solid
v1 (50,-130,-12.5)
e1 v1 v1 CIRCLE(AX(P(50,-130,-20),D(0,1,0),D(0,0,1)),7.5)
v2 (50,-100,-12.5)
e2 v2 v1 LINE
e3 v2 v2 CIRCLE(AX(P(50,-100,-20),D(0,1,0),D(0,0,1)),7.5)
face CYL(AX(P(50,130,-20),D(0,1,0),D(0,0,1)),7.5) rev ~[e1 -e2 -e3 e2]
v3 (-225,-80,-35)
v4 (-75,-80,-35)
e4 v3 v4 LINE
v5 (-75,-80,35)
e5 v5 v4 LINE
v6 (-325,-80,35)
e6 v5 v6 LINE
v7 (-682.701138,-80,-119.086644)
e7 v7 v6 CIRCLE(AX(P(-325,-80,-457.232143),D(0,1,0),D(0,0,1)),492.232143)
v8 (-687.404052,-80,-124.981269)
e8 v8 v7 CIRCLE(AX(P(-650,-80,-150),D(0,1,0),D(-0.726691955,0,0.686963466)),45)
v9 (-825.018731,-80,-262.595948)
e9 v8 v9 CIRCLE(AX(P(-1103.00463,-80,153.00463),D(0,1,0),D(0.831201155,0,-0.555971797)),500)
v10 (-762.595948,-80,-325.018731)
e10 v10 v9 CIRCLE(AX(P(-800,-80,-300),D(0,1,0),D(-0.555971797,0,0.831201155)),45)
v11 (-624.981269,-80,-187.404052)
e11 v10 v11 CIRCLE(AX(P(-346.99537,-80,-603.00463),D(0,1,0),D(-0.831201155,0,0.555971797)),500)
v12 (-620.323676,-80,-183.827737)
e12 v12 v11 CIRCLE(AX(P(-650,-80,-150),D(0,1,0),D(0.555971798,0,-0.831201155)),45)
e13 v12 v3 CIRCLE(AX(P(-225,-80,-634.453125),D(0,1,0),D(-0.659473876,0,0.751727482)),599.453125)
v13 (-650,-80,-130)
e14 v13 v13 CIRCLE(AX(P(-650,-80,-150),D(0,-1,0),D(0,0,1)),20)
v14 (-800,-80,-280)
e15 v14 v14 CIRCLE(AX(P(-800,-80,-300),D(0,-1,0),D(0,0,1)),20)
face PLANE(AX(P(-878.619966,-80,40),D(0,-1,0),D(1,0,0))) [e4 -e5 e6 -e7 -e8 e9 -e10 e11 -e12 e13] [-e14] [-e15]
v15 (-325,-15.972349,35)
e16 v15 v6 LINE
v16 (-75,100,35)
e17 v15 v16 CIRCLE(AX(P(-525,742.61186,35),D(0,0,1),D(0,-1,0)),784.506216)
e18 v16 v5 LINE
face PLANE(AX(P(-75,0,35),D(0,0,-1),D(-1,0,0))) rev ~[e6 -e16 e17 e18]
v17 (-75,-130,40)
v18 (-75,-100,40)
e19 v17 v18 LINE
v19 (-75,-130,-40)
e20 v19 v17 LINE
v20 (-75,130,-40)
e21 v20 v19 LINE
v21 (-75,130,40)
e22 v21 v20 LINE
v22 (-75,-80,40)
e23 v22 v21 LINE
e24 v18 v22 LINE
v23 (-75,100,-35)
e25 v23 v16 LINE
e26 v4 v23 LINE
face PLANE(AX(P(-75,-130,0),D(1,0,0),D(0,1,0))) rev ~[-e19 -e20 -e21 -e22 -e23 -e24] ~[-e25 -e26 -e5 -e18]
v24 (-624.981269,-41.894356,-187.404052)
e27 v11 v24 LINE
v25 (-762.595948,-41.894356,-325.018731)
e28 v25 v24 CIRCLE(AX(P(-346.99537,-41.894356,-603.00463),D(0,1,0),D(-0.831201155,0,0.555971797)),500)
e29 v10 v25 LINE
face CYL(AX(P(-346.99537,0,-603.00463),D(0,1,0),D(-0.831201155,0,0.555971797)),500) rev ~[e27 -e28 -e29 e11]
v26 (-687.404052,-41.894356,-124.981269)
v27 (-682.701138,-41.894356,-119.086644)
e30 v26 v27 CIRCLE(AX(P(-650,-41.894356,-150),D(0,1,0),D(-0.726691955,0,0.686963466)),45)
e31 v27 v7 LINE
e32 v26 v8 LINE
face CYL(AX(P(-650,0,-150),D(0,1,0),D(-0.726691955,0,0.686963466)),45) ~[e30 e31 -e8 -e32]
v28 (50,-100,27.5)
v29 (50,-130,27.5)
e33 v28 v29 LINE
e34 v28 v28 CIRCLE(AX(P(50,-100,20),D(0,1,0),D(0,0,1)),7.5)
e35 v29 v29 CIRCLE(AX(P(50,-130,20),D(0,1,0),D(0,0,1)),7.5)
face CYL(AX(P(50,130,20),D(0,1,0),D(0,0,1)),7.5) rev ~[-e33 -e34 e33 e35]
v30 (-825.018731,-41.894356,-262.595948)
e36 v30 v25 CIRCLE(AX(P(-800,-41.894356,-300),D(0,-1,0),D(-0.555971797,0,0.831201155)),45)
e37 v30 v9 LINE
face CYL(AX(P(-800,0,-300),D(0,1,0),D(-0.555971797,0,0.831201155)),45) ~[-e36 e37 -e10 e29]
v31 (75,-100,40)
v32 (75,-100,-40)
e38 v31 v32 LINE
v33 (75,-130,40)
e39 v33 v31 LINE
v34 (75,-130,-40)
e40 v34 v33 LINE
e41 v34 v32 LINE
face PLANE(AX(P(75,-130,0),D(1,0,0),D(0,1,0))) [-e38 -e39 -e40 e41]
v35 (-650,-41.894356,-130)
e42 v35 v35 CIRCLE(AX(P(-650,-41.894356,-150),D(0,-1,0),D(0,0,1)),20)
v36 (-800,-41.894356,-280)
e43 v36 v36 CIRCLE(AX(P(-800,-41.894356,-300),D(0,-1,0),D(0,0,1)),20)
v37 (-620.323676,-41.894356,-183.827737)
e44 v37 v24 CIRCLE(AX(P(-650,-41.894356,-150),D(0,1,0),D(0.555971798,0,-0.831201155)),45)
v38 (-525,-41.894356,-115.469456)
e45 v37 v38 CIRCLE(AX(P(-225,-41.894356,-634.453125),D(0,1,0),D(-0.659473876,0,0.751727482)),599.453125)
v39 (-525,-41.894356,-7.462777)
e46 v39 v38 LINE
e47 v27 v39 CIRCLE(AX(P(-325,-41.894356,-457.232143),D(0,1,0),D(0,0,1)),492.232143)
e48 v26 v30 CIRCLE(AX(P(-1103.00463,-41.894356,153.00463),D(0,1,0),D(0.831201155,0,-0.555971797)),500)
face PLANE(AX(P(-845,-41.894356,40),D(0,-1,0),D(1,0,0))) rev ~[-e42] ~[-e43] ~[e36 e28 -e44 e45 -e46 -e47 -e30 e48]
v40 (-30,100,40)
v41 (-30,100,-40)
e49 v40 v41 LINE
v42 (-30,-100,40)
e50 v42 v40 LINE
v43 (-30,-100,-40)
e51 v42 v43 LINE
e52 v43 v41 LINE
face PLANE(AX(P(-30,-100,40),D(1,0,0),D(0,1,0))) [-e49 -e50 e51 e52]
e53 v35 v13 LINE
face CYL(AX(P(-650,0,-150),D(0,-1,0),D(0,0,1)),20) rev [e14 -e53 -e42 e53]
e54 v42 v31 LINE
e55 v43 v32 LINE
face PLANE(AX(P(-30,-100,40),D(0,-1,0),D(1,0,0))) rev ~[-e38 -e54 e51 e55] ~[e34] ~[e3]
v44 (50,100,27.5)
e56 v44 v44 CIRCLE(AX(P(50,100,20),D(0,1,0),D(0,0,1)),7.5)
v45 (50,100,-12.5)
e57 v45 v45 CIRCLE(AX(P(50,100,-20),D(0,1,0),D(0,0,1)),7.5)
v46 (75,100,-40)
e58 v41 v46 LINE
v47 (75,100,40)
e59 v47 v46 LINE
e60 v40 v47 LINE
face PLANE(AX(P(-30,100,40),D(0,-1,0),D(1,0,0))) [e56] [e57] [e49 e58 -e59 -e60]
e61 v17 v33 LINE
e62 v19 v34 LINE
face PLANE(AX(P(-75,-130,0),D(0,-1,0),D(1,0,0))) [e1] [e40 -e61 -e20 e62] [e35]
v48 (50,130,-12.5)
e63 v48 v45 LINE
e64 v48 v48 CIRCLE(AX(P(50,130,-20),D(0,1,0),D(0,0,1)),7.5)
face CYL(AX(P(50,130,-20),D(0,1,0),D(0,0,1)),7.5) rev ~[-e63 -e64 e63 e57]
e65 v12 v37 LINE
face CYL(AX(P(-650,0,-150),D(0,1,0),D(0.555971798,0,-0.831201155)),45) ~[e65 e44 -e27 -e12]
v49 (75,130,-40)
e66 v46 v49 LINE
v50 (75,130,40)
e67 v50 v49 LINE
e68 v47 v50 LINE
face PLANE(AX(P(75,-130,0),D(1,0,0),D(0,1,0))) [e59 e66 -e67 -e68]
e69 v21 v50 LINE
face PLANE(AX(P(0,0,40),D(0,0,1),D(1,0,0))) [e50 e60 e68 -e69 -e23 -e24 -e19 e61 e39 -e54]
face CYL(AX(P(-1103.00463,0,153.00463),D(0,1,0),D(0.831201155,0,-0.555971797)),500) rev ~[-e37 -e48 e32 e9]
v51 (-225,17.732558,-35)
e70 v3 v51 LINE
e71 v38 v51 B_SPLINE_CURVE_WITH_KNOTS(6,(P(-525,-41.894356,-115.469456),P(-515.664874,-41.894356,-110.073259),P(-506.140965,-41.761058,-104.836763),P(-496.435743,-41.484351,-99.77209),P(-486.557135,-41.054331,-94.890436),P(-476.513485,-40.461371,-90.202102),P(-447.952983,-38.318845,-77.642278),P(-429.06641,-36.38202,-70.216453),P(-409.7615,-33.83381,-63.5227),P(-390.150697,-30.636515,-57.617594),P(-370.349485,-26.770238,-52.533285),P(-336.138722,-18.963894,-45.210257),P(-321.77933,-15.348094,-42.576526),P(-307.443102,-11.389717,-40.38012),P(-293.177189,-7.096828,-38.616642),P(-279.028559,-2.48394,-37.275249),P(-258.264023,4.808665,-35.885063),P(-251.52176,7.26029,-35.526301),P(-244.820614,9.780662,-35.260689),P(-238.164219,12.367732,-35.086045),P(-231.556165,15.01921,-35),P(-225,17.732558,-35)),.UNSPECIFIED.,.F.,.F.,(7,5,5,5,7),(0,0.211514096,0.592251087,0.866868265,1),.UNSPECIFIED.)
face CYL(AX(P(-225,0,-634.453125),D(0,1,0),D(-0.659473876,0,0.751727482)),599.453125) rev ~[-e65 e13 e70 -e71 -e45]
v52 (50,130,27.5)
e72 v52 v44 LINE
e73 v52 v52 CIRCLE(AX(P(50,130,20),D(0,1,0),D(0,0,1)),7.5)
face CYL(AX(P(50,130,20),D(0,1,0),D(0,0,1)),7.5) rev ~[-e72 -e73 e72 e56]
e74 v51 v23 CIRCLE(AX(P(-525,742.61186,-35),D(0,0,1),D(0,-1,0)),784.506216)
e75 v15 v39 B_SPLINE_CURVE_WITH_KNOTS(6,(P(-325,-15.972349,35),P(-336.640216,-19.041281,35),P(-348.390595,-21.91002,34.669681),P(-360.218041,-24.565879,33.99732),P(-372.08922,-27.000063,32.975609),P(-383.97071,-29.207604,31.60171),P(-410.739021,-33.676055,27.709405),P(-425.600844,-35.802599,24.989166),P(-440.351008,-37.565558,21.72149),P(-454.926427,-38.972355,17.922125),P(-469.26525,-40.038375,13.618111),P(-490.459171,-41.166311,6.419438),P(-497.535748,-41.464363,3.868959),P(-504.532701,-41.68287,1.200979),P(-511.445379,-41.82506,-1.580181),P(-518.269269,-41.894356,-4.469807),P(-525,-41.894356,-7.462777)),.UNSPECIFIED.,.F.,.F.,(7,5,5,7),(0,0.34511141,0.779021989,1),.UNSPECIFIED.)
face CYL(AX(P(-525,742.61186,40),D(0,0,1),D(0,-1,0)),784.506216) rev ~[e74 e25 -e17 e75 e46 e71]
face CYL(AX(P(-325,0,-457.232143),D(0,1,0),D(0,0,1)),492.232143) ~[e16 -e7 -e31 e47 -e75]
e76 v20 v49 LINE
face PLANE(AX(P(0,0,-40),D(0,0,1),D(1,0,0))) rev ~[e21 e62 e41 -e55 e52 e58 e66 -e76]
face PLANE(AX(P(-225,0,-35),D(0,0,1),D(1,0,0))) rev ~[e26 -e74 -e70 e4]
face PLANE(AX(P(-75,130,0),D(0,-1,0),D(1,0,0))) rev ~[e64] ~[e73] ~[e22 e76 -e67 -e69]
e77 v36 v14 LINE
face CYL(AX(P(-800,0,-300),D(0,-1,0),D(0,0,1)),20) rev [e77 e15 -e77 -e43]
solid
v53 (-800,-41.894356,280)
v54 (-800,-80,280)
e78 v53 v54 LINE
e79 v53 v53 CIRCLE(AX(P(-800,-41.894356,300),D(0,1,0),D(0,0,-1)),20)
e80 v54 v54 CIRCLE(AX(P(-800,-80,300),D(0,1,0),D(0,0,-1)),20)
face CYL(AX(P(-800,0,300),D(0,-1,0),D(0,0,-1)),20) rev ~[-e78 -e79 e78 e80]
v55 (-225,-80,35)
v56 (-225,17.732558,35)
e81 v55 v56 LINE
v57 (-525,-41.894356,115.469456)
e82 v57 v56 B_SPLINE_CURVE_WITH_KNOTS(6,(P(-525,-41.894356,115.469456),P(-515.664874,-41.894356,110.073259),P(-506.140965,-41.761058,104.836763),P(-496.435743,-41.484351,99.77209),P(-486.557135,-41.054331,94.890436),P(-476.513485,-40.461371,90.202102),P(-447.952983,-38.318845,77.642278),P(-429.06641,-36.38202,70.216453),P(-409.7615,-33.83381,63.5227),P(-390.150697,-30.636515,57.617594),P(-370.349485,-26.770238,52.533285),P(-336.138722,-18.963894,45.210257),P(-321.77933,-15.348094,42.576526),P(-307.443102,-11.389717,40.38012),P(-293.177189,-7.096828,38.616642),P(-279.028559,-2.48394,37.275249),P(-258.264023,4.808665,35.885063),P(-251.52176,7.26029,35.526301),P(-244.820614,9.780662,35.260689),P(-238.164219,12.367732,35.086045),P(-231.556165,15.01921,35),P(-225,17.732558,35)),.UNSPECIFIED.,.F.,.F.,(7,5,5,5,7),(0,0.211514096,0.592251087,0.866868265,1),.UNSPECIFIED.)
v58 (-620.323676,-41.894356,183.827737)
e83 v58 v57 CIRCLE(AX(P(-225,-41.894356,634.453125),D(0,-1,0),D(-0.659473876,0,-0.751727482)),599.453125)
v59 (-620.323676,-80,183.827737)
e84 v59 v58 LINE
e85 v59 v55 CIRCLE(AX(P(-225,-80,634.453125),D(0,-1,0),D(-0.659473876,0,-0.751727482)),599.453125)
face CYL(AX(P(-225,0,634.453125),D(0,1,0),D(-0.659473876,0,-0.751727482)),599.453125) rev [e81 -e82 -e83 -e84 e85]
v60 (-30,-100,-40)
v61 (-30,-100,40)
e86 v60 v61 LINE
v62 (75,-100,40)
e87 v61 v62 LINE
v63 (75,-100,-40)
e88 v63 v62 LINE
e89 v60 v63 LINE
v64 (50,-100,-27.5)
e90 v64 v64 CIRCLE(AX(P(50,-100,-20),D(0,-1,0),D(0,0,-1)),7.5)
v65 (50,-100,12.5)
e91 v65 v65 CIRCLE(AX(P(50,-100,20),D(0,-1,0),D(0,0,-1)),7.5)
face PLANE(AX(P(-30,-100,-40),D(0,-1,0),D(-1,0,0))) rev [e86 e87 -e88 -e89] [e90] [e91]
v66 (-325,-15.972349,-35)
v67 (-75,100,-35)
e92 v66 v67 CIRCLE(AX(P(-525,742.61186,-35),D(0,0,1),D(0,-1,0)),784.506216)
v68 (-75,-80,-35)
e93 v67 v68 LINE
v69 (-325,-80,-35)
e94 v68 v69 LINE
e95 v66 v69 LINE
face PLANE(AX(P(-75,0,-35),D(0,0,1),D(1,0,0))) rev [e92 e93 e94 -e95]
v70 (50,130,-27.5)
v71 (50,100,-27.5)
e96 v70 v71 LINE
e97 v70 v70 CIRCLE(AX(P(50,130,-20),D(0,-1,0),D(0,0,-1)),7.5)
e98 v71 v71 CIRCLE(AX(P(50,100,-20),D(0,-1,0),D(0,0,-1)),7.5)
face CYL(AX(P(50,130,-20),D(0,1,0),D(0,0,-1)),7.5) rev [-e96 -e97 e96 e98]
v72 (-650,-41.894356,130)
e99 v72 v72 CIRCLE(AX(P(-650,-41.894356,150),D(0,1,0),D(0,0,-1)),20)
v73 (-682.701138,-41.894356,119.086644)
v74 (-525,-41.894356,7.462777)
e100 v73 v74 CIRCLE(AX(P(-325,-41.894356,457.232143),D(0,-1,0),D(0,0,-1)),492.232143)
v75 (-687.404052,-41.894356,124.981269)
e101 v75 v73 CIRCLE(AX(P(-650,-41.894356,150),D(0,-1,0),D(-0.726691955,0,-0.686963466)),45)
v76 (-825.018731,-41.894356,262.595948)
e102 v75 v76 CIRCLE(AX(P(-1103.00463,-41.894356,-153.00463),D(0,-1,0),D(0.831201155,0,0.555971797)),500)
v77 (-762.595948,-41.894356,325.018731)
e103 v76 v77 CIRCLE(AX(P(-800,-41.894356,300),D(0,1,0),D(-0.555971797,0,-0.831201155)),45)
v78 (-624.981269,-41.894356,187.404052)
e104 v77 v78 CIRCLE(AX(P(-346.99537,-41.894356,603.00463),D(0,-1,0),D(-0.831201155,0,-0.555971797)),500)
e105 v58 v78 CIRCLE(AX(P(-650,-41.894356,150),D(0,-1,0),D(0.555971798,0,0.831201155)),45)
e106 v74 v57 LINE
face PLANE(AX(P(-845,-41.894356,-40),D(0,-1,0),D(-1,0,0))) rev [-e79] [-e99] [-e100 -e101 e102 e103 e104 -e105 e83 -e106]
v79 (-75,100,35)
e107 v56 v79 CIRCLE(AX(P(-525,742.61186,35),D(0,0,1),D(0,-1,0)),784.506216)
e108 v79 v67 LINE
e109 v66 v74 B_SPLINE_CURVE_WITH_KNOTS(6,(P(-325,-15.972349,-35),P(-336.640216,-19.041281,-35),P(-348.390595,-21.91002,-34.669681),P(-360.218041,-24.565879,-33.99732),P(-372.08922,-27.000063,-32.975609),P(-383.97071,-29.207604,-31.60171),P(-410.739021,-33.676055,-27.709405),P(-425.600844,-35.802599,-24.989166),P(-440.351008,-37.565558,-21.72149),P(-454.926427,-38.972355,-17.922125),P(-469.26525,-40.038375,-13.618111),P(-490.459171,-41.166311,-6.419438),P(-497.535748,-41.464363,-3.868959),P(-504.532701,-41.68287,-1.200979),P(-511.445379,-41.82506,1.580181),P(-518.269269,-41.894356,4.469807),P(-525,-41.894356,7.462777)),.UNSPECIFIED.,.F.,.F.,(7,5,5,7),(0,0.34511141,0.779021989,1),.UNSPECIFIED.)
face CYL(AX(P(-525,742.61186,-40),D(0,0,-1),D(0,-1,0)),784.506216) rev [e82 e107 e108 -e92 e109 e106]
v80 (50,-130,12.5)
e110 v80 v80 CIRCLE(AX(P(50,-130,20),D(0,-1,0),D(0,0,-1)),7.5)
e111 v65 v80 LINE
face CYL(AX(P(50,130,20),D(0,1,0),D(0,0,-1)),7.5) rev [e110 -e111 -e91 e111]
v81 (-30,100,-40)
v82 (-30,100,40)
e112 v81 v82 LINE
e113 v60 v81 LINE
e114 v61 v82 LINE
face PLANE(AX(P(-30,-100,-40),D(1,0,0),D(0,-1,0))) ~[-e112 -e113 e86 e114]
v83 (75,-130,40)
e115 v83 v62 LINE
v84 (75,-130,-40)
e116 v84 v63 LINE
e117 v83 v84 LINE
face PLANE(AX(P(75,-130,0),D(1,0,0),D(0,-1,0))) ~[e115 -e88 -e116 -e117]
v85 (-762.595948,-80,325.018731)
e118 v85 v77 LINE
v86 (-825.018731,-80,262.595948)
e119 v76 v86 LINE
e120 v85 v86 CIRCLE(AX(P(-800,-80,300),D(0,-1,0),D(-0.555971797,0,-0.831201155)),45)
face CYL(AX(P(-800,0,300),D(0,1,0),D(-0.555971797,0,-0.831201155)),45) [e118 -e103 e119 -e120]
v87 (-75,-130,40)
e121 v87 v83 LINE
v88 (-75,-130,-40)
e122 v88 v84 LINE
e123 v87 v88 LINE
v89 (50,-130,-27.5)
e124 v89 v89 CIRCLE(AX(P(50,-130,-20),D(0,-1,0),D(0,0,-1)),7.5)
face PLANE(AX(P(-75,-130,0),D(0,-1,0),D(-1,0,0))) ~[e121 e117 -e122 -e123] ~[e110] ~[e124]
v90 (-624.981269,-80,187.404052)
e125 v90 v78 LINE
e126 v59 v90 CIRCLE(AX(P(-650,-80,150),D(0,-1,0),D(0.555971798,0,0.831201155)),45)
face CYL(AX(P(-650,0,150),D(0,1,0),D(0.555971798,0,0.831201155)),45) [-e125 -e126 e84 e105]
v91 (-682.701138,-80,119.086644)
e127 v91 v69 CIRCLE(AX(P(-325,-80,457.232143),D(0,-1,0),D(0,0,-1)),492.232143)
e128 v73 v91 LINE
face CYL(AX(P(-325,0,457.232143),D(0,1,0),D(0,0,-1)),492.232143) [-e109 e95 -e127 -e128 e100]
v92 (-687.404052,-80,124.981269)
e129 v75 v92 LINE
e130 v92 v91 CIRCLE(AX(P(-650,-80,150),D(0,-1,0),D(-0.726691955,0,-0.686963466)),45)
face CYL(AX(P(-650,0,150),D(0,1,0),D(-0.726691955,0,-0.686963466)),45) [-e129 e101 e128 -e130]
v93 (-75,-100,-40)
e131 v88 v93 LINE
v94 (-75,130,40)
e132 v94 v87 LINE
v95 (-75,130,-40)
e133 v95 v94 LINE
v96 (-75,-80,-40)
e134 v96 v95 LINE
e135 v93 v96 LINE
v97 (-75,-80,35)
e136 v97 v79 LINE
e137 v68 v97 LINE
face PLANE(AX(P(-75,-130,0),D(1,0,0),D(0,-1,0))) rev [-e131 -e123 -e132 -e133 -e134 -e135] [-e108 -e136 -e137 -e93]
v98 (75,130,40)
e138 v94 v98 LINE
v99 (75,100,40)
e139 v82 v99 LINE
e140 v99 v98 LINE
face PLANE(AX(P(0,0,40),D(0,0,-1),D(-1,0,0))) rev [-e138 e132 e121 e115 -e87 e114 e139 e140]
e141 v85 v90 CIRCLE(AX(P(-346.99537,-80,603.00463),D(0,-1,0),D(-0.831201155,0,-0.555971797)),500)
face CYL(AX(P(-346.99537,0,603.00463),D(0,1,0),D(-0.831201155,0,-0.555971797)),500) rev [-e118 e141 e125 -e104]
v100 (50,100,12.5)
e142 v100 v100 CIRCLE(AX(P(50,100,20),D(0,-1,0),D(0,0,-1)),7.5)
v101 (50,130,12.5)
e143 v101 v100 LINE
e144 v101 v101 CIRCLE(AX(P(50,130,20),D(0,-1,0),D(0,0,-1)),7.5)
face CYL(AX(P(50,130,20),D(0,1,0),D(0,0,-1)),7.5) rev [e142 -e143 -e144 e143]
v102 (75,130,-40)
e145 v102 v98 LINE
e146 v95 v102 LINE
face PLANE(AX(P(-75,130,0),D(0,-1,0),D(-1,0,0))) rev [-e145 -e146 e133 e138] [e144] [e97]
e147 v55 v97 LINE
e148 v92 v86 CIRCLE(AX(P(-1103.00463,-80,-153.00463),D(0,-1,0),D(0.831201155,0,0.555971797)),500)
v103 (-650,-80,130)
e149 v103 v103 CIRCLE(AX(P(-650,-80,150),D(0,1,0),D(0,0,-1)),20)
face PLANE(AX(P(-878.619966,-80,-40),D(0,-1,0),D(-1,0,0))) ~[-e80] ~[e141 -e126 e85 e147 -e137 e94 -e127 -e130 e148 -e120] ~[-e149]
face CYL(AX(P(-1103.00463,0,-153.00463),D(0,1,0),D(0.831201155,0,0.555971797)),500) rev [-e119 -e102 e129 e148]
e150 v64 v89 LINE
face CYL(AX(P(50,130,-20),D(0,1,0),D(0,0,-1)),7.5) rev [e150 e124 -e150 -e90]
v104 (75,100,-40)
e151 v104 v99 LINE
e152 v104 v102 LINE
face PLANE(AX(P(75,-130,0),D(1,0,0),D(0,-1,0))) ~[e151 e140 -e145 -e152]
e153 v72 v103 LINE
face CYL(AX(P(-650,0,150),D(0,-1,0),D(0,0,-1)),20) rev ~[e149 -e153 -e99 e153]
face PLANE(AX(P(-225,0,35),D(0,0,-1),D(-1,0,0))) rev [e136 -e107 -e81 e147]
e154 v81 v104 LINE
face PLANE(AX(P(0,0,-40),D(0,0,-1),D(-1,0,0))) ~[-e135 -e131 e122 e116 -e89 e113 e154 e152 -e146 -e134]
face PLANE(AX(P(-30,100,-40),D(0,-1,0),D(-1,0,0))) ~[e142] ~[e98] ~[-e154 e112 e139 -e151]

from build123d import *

# Parameters (mm, degrees)
SKETCH1_W           = 150
SKETCH1_H           = 260
BOSS_EXTRUDE1_DEPTH = 40
SKETCH2_W           = 210
SKETCH2_H           = 200
CUT_EXTRUDE1_DEPTH  = 171.073513517
SKETCH3_R           = 20
BOSS_EXTRUDE2_DEPTH = 100
SKETCH4_W           = 803.619965953
SKETCH4_H           = 20
CUT_EXTRUDE2_DEPTH  = 938.629990988
SKETCH5_R           = 7.5
CUT_EXTRUDE3_DEPTH  = 950.025816298


with BuildPart() as part:
    # Sketch1 → Boss-Extrude1 (new, symmetric)
    with BuildSketch(Plane.XY):
        Rectangle(SKETCH1_W, SKETCH1_H)
    extrude(amount=BOSS_EXTRUDE1_DEPTH, both=True)

    # Sketch2 → Cut-Extrude1 (cut, through all)
    with BuildSketch(Plane.XY.offset(40)):
        with Locations((75, 0)):
            Rectangle(SKETCH2_W, SKETCH2_H)
    extrude(amount=-CUT_EXTRUDE1_DEPTH, mode=Mode.SUBTRACT)

    # Sketch3 → Boss-Extrude2 (add, symmetric)
    with BuildSketch(Plane(origin=(0, 0, 0), x_dir=(1, 0, 0), z_dir=(0, 1, 0))):
        with BuildLine():
            Line((-75, 35), (-75, -35))
            Line((-75, -35), (-325, -35))
            ThreePointArc((-325, -35), (-519.738798114, 5.159932949), (-682.701137952, 119.086644041))
            ThreePointArc((-682.701137952, 119.086644041), (-685.176285552, 121.935272409), (-687.404051985, 124.981269115))
            ThreePointArc((-687.404051985, 124.981269115), (-749.451239008, 200.548760992), (-825.018730885, 262.595948015))
            ThreePointArc((-825.018730885, 262.595948015), (-831.819805153, 331.819805153), (-762.595948015, 325.018730885))
            ThreePointArc((-762.595948015, 325.018730885), (-700.548760992, 249.451239008), (-624.981269115, 187.404051985))
            ThreePointArc((-624.981269115, 187.404051985), (-622.594074072, 185.691949008), (-620.323675597, 183.827736695))
            ThreePointArc((-620.323675597, 183.827736695), (-436.205174947, 73.439379047), (-225, 35))
            Line((-225, 35), (-75, 35))
        make_face()
        with Locations(Location((-800, 300, 0), (0, 0, 270))):
            Circle(SKETCH3_R, mode=Mode.SUBTRACT)
        with Locations(Location((-650, 150, 0), (0, 0, 270))):
            Circle(SKETCH3_R, mode=Mode.SUBTRACT)
    extrude(amount=BOSS_EXTRUDE2_DEPTH, both=True)

    # Sketch4 → Cut-Extrude2 (cut, through all)
    with BuildSketch(Plane.XY.offset(40)):
        with BuildLine():
            Line((-845, -41.894355792), (-525, -41.894355792))
            ThreePointArc((-525, -41.894355792), (-289.079458183, -5.58029484), (-75, 100))
            Line((-75, 100), (-75, 271.543377567))
            Line((-75, 271.543377567), (-930.312531667, 271.543377567))
            Line((-930.312531667, 271.543377567), (-961.602268008, -20.942543752))
            Line((-961.602268008, -20.942543752), (-845, -41.894355792))
        make_face()
        with Locations((-476.809982977, -90)):
            Rectangle(SKETCH4_W, SKETCH4_H)
    extrude(amount=-CUT_EXTRUDE2_DEPTH, mode=Mode.SUBTRACT)

    # Sketch5 → Cut-Extrude3 (cut, through all)
    with BuildSketch(Plane(origin=(0, 130, 0), x_dir=(1, 0, 0), z_dir=(0, 1, 0))):
        with Locations(Location((50, 20, 0), (0, 0, 270))):
            Circle(SKETCH5_R)
        with Locations(Location((50, -20, 0), (0, 0, 270))):
            Circle(SKETCH5_R)
    extrude(amount=-CUT_EXTRUDE3_DEPTH, mode=Mode.SUBTRACT)


with BuildPart() as body_2:
    # Mirror1: mirrored copy
    add(part.part.mirror(Plane.XY))


solid = Compound([part.part, body_2.part])
